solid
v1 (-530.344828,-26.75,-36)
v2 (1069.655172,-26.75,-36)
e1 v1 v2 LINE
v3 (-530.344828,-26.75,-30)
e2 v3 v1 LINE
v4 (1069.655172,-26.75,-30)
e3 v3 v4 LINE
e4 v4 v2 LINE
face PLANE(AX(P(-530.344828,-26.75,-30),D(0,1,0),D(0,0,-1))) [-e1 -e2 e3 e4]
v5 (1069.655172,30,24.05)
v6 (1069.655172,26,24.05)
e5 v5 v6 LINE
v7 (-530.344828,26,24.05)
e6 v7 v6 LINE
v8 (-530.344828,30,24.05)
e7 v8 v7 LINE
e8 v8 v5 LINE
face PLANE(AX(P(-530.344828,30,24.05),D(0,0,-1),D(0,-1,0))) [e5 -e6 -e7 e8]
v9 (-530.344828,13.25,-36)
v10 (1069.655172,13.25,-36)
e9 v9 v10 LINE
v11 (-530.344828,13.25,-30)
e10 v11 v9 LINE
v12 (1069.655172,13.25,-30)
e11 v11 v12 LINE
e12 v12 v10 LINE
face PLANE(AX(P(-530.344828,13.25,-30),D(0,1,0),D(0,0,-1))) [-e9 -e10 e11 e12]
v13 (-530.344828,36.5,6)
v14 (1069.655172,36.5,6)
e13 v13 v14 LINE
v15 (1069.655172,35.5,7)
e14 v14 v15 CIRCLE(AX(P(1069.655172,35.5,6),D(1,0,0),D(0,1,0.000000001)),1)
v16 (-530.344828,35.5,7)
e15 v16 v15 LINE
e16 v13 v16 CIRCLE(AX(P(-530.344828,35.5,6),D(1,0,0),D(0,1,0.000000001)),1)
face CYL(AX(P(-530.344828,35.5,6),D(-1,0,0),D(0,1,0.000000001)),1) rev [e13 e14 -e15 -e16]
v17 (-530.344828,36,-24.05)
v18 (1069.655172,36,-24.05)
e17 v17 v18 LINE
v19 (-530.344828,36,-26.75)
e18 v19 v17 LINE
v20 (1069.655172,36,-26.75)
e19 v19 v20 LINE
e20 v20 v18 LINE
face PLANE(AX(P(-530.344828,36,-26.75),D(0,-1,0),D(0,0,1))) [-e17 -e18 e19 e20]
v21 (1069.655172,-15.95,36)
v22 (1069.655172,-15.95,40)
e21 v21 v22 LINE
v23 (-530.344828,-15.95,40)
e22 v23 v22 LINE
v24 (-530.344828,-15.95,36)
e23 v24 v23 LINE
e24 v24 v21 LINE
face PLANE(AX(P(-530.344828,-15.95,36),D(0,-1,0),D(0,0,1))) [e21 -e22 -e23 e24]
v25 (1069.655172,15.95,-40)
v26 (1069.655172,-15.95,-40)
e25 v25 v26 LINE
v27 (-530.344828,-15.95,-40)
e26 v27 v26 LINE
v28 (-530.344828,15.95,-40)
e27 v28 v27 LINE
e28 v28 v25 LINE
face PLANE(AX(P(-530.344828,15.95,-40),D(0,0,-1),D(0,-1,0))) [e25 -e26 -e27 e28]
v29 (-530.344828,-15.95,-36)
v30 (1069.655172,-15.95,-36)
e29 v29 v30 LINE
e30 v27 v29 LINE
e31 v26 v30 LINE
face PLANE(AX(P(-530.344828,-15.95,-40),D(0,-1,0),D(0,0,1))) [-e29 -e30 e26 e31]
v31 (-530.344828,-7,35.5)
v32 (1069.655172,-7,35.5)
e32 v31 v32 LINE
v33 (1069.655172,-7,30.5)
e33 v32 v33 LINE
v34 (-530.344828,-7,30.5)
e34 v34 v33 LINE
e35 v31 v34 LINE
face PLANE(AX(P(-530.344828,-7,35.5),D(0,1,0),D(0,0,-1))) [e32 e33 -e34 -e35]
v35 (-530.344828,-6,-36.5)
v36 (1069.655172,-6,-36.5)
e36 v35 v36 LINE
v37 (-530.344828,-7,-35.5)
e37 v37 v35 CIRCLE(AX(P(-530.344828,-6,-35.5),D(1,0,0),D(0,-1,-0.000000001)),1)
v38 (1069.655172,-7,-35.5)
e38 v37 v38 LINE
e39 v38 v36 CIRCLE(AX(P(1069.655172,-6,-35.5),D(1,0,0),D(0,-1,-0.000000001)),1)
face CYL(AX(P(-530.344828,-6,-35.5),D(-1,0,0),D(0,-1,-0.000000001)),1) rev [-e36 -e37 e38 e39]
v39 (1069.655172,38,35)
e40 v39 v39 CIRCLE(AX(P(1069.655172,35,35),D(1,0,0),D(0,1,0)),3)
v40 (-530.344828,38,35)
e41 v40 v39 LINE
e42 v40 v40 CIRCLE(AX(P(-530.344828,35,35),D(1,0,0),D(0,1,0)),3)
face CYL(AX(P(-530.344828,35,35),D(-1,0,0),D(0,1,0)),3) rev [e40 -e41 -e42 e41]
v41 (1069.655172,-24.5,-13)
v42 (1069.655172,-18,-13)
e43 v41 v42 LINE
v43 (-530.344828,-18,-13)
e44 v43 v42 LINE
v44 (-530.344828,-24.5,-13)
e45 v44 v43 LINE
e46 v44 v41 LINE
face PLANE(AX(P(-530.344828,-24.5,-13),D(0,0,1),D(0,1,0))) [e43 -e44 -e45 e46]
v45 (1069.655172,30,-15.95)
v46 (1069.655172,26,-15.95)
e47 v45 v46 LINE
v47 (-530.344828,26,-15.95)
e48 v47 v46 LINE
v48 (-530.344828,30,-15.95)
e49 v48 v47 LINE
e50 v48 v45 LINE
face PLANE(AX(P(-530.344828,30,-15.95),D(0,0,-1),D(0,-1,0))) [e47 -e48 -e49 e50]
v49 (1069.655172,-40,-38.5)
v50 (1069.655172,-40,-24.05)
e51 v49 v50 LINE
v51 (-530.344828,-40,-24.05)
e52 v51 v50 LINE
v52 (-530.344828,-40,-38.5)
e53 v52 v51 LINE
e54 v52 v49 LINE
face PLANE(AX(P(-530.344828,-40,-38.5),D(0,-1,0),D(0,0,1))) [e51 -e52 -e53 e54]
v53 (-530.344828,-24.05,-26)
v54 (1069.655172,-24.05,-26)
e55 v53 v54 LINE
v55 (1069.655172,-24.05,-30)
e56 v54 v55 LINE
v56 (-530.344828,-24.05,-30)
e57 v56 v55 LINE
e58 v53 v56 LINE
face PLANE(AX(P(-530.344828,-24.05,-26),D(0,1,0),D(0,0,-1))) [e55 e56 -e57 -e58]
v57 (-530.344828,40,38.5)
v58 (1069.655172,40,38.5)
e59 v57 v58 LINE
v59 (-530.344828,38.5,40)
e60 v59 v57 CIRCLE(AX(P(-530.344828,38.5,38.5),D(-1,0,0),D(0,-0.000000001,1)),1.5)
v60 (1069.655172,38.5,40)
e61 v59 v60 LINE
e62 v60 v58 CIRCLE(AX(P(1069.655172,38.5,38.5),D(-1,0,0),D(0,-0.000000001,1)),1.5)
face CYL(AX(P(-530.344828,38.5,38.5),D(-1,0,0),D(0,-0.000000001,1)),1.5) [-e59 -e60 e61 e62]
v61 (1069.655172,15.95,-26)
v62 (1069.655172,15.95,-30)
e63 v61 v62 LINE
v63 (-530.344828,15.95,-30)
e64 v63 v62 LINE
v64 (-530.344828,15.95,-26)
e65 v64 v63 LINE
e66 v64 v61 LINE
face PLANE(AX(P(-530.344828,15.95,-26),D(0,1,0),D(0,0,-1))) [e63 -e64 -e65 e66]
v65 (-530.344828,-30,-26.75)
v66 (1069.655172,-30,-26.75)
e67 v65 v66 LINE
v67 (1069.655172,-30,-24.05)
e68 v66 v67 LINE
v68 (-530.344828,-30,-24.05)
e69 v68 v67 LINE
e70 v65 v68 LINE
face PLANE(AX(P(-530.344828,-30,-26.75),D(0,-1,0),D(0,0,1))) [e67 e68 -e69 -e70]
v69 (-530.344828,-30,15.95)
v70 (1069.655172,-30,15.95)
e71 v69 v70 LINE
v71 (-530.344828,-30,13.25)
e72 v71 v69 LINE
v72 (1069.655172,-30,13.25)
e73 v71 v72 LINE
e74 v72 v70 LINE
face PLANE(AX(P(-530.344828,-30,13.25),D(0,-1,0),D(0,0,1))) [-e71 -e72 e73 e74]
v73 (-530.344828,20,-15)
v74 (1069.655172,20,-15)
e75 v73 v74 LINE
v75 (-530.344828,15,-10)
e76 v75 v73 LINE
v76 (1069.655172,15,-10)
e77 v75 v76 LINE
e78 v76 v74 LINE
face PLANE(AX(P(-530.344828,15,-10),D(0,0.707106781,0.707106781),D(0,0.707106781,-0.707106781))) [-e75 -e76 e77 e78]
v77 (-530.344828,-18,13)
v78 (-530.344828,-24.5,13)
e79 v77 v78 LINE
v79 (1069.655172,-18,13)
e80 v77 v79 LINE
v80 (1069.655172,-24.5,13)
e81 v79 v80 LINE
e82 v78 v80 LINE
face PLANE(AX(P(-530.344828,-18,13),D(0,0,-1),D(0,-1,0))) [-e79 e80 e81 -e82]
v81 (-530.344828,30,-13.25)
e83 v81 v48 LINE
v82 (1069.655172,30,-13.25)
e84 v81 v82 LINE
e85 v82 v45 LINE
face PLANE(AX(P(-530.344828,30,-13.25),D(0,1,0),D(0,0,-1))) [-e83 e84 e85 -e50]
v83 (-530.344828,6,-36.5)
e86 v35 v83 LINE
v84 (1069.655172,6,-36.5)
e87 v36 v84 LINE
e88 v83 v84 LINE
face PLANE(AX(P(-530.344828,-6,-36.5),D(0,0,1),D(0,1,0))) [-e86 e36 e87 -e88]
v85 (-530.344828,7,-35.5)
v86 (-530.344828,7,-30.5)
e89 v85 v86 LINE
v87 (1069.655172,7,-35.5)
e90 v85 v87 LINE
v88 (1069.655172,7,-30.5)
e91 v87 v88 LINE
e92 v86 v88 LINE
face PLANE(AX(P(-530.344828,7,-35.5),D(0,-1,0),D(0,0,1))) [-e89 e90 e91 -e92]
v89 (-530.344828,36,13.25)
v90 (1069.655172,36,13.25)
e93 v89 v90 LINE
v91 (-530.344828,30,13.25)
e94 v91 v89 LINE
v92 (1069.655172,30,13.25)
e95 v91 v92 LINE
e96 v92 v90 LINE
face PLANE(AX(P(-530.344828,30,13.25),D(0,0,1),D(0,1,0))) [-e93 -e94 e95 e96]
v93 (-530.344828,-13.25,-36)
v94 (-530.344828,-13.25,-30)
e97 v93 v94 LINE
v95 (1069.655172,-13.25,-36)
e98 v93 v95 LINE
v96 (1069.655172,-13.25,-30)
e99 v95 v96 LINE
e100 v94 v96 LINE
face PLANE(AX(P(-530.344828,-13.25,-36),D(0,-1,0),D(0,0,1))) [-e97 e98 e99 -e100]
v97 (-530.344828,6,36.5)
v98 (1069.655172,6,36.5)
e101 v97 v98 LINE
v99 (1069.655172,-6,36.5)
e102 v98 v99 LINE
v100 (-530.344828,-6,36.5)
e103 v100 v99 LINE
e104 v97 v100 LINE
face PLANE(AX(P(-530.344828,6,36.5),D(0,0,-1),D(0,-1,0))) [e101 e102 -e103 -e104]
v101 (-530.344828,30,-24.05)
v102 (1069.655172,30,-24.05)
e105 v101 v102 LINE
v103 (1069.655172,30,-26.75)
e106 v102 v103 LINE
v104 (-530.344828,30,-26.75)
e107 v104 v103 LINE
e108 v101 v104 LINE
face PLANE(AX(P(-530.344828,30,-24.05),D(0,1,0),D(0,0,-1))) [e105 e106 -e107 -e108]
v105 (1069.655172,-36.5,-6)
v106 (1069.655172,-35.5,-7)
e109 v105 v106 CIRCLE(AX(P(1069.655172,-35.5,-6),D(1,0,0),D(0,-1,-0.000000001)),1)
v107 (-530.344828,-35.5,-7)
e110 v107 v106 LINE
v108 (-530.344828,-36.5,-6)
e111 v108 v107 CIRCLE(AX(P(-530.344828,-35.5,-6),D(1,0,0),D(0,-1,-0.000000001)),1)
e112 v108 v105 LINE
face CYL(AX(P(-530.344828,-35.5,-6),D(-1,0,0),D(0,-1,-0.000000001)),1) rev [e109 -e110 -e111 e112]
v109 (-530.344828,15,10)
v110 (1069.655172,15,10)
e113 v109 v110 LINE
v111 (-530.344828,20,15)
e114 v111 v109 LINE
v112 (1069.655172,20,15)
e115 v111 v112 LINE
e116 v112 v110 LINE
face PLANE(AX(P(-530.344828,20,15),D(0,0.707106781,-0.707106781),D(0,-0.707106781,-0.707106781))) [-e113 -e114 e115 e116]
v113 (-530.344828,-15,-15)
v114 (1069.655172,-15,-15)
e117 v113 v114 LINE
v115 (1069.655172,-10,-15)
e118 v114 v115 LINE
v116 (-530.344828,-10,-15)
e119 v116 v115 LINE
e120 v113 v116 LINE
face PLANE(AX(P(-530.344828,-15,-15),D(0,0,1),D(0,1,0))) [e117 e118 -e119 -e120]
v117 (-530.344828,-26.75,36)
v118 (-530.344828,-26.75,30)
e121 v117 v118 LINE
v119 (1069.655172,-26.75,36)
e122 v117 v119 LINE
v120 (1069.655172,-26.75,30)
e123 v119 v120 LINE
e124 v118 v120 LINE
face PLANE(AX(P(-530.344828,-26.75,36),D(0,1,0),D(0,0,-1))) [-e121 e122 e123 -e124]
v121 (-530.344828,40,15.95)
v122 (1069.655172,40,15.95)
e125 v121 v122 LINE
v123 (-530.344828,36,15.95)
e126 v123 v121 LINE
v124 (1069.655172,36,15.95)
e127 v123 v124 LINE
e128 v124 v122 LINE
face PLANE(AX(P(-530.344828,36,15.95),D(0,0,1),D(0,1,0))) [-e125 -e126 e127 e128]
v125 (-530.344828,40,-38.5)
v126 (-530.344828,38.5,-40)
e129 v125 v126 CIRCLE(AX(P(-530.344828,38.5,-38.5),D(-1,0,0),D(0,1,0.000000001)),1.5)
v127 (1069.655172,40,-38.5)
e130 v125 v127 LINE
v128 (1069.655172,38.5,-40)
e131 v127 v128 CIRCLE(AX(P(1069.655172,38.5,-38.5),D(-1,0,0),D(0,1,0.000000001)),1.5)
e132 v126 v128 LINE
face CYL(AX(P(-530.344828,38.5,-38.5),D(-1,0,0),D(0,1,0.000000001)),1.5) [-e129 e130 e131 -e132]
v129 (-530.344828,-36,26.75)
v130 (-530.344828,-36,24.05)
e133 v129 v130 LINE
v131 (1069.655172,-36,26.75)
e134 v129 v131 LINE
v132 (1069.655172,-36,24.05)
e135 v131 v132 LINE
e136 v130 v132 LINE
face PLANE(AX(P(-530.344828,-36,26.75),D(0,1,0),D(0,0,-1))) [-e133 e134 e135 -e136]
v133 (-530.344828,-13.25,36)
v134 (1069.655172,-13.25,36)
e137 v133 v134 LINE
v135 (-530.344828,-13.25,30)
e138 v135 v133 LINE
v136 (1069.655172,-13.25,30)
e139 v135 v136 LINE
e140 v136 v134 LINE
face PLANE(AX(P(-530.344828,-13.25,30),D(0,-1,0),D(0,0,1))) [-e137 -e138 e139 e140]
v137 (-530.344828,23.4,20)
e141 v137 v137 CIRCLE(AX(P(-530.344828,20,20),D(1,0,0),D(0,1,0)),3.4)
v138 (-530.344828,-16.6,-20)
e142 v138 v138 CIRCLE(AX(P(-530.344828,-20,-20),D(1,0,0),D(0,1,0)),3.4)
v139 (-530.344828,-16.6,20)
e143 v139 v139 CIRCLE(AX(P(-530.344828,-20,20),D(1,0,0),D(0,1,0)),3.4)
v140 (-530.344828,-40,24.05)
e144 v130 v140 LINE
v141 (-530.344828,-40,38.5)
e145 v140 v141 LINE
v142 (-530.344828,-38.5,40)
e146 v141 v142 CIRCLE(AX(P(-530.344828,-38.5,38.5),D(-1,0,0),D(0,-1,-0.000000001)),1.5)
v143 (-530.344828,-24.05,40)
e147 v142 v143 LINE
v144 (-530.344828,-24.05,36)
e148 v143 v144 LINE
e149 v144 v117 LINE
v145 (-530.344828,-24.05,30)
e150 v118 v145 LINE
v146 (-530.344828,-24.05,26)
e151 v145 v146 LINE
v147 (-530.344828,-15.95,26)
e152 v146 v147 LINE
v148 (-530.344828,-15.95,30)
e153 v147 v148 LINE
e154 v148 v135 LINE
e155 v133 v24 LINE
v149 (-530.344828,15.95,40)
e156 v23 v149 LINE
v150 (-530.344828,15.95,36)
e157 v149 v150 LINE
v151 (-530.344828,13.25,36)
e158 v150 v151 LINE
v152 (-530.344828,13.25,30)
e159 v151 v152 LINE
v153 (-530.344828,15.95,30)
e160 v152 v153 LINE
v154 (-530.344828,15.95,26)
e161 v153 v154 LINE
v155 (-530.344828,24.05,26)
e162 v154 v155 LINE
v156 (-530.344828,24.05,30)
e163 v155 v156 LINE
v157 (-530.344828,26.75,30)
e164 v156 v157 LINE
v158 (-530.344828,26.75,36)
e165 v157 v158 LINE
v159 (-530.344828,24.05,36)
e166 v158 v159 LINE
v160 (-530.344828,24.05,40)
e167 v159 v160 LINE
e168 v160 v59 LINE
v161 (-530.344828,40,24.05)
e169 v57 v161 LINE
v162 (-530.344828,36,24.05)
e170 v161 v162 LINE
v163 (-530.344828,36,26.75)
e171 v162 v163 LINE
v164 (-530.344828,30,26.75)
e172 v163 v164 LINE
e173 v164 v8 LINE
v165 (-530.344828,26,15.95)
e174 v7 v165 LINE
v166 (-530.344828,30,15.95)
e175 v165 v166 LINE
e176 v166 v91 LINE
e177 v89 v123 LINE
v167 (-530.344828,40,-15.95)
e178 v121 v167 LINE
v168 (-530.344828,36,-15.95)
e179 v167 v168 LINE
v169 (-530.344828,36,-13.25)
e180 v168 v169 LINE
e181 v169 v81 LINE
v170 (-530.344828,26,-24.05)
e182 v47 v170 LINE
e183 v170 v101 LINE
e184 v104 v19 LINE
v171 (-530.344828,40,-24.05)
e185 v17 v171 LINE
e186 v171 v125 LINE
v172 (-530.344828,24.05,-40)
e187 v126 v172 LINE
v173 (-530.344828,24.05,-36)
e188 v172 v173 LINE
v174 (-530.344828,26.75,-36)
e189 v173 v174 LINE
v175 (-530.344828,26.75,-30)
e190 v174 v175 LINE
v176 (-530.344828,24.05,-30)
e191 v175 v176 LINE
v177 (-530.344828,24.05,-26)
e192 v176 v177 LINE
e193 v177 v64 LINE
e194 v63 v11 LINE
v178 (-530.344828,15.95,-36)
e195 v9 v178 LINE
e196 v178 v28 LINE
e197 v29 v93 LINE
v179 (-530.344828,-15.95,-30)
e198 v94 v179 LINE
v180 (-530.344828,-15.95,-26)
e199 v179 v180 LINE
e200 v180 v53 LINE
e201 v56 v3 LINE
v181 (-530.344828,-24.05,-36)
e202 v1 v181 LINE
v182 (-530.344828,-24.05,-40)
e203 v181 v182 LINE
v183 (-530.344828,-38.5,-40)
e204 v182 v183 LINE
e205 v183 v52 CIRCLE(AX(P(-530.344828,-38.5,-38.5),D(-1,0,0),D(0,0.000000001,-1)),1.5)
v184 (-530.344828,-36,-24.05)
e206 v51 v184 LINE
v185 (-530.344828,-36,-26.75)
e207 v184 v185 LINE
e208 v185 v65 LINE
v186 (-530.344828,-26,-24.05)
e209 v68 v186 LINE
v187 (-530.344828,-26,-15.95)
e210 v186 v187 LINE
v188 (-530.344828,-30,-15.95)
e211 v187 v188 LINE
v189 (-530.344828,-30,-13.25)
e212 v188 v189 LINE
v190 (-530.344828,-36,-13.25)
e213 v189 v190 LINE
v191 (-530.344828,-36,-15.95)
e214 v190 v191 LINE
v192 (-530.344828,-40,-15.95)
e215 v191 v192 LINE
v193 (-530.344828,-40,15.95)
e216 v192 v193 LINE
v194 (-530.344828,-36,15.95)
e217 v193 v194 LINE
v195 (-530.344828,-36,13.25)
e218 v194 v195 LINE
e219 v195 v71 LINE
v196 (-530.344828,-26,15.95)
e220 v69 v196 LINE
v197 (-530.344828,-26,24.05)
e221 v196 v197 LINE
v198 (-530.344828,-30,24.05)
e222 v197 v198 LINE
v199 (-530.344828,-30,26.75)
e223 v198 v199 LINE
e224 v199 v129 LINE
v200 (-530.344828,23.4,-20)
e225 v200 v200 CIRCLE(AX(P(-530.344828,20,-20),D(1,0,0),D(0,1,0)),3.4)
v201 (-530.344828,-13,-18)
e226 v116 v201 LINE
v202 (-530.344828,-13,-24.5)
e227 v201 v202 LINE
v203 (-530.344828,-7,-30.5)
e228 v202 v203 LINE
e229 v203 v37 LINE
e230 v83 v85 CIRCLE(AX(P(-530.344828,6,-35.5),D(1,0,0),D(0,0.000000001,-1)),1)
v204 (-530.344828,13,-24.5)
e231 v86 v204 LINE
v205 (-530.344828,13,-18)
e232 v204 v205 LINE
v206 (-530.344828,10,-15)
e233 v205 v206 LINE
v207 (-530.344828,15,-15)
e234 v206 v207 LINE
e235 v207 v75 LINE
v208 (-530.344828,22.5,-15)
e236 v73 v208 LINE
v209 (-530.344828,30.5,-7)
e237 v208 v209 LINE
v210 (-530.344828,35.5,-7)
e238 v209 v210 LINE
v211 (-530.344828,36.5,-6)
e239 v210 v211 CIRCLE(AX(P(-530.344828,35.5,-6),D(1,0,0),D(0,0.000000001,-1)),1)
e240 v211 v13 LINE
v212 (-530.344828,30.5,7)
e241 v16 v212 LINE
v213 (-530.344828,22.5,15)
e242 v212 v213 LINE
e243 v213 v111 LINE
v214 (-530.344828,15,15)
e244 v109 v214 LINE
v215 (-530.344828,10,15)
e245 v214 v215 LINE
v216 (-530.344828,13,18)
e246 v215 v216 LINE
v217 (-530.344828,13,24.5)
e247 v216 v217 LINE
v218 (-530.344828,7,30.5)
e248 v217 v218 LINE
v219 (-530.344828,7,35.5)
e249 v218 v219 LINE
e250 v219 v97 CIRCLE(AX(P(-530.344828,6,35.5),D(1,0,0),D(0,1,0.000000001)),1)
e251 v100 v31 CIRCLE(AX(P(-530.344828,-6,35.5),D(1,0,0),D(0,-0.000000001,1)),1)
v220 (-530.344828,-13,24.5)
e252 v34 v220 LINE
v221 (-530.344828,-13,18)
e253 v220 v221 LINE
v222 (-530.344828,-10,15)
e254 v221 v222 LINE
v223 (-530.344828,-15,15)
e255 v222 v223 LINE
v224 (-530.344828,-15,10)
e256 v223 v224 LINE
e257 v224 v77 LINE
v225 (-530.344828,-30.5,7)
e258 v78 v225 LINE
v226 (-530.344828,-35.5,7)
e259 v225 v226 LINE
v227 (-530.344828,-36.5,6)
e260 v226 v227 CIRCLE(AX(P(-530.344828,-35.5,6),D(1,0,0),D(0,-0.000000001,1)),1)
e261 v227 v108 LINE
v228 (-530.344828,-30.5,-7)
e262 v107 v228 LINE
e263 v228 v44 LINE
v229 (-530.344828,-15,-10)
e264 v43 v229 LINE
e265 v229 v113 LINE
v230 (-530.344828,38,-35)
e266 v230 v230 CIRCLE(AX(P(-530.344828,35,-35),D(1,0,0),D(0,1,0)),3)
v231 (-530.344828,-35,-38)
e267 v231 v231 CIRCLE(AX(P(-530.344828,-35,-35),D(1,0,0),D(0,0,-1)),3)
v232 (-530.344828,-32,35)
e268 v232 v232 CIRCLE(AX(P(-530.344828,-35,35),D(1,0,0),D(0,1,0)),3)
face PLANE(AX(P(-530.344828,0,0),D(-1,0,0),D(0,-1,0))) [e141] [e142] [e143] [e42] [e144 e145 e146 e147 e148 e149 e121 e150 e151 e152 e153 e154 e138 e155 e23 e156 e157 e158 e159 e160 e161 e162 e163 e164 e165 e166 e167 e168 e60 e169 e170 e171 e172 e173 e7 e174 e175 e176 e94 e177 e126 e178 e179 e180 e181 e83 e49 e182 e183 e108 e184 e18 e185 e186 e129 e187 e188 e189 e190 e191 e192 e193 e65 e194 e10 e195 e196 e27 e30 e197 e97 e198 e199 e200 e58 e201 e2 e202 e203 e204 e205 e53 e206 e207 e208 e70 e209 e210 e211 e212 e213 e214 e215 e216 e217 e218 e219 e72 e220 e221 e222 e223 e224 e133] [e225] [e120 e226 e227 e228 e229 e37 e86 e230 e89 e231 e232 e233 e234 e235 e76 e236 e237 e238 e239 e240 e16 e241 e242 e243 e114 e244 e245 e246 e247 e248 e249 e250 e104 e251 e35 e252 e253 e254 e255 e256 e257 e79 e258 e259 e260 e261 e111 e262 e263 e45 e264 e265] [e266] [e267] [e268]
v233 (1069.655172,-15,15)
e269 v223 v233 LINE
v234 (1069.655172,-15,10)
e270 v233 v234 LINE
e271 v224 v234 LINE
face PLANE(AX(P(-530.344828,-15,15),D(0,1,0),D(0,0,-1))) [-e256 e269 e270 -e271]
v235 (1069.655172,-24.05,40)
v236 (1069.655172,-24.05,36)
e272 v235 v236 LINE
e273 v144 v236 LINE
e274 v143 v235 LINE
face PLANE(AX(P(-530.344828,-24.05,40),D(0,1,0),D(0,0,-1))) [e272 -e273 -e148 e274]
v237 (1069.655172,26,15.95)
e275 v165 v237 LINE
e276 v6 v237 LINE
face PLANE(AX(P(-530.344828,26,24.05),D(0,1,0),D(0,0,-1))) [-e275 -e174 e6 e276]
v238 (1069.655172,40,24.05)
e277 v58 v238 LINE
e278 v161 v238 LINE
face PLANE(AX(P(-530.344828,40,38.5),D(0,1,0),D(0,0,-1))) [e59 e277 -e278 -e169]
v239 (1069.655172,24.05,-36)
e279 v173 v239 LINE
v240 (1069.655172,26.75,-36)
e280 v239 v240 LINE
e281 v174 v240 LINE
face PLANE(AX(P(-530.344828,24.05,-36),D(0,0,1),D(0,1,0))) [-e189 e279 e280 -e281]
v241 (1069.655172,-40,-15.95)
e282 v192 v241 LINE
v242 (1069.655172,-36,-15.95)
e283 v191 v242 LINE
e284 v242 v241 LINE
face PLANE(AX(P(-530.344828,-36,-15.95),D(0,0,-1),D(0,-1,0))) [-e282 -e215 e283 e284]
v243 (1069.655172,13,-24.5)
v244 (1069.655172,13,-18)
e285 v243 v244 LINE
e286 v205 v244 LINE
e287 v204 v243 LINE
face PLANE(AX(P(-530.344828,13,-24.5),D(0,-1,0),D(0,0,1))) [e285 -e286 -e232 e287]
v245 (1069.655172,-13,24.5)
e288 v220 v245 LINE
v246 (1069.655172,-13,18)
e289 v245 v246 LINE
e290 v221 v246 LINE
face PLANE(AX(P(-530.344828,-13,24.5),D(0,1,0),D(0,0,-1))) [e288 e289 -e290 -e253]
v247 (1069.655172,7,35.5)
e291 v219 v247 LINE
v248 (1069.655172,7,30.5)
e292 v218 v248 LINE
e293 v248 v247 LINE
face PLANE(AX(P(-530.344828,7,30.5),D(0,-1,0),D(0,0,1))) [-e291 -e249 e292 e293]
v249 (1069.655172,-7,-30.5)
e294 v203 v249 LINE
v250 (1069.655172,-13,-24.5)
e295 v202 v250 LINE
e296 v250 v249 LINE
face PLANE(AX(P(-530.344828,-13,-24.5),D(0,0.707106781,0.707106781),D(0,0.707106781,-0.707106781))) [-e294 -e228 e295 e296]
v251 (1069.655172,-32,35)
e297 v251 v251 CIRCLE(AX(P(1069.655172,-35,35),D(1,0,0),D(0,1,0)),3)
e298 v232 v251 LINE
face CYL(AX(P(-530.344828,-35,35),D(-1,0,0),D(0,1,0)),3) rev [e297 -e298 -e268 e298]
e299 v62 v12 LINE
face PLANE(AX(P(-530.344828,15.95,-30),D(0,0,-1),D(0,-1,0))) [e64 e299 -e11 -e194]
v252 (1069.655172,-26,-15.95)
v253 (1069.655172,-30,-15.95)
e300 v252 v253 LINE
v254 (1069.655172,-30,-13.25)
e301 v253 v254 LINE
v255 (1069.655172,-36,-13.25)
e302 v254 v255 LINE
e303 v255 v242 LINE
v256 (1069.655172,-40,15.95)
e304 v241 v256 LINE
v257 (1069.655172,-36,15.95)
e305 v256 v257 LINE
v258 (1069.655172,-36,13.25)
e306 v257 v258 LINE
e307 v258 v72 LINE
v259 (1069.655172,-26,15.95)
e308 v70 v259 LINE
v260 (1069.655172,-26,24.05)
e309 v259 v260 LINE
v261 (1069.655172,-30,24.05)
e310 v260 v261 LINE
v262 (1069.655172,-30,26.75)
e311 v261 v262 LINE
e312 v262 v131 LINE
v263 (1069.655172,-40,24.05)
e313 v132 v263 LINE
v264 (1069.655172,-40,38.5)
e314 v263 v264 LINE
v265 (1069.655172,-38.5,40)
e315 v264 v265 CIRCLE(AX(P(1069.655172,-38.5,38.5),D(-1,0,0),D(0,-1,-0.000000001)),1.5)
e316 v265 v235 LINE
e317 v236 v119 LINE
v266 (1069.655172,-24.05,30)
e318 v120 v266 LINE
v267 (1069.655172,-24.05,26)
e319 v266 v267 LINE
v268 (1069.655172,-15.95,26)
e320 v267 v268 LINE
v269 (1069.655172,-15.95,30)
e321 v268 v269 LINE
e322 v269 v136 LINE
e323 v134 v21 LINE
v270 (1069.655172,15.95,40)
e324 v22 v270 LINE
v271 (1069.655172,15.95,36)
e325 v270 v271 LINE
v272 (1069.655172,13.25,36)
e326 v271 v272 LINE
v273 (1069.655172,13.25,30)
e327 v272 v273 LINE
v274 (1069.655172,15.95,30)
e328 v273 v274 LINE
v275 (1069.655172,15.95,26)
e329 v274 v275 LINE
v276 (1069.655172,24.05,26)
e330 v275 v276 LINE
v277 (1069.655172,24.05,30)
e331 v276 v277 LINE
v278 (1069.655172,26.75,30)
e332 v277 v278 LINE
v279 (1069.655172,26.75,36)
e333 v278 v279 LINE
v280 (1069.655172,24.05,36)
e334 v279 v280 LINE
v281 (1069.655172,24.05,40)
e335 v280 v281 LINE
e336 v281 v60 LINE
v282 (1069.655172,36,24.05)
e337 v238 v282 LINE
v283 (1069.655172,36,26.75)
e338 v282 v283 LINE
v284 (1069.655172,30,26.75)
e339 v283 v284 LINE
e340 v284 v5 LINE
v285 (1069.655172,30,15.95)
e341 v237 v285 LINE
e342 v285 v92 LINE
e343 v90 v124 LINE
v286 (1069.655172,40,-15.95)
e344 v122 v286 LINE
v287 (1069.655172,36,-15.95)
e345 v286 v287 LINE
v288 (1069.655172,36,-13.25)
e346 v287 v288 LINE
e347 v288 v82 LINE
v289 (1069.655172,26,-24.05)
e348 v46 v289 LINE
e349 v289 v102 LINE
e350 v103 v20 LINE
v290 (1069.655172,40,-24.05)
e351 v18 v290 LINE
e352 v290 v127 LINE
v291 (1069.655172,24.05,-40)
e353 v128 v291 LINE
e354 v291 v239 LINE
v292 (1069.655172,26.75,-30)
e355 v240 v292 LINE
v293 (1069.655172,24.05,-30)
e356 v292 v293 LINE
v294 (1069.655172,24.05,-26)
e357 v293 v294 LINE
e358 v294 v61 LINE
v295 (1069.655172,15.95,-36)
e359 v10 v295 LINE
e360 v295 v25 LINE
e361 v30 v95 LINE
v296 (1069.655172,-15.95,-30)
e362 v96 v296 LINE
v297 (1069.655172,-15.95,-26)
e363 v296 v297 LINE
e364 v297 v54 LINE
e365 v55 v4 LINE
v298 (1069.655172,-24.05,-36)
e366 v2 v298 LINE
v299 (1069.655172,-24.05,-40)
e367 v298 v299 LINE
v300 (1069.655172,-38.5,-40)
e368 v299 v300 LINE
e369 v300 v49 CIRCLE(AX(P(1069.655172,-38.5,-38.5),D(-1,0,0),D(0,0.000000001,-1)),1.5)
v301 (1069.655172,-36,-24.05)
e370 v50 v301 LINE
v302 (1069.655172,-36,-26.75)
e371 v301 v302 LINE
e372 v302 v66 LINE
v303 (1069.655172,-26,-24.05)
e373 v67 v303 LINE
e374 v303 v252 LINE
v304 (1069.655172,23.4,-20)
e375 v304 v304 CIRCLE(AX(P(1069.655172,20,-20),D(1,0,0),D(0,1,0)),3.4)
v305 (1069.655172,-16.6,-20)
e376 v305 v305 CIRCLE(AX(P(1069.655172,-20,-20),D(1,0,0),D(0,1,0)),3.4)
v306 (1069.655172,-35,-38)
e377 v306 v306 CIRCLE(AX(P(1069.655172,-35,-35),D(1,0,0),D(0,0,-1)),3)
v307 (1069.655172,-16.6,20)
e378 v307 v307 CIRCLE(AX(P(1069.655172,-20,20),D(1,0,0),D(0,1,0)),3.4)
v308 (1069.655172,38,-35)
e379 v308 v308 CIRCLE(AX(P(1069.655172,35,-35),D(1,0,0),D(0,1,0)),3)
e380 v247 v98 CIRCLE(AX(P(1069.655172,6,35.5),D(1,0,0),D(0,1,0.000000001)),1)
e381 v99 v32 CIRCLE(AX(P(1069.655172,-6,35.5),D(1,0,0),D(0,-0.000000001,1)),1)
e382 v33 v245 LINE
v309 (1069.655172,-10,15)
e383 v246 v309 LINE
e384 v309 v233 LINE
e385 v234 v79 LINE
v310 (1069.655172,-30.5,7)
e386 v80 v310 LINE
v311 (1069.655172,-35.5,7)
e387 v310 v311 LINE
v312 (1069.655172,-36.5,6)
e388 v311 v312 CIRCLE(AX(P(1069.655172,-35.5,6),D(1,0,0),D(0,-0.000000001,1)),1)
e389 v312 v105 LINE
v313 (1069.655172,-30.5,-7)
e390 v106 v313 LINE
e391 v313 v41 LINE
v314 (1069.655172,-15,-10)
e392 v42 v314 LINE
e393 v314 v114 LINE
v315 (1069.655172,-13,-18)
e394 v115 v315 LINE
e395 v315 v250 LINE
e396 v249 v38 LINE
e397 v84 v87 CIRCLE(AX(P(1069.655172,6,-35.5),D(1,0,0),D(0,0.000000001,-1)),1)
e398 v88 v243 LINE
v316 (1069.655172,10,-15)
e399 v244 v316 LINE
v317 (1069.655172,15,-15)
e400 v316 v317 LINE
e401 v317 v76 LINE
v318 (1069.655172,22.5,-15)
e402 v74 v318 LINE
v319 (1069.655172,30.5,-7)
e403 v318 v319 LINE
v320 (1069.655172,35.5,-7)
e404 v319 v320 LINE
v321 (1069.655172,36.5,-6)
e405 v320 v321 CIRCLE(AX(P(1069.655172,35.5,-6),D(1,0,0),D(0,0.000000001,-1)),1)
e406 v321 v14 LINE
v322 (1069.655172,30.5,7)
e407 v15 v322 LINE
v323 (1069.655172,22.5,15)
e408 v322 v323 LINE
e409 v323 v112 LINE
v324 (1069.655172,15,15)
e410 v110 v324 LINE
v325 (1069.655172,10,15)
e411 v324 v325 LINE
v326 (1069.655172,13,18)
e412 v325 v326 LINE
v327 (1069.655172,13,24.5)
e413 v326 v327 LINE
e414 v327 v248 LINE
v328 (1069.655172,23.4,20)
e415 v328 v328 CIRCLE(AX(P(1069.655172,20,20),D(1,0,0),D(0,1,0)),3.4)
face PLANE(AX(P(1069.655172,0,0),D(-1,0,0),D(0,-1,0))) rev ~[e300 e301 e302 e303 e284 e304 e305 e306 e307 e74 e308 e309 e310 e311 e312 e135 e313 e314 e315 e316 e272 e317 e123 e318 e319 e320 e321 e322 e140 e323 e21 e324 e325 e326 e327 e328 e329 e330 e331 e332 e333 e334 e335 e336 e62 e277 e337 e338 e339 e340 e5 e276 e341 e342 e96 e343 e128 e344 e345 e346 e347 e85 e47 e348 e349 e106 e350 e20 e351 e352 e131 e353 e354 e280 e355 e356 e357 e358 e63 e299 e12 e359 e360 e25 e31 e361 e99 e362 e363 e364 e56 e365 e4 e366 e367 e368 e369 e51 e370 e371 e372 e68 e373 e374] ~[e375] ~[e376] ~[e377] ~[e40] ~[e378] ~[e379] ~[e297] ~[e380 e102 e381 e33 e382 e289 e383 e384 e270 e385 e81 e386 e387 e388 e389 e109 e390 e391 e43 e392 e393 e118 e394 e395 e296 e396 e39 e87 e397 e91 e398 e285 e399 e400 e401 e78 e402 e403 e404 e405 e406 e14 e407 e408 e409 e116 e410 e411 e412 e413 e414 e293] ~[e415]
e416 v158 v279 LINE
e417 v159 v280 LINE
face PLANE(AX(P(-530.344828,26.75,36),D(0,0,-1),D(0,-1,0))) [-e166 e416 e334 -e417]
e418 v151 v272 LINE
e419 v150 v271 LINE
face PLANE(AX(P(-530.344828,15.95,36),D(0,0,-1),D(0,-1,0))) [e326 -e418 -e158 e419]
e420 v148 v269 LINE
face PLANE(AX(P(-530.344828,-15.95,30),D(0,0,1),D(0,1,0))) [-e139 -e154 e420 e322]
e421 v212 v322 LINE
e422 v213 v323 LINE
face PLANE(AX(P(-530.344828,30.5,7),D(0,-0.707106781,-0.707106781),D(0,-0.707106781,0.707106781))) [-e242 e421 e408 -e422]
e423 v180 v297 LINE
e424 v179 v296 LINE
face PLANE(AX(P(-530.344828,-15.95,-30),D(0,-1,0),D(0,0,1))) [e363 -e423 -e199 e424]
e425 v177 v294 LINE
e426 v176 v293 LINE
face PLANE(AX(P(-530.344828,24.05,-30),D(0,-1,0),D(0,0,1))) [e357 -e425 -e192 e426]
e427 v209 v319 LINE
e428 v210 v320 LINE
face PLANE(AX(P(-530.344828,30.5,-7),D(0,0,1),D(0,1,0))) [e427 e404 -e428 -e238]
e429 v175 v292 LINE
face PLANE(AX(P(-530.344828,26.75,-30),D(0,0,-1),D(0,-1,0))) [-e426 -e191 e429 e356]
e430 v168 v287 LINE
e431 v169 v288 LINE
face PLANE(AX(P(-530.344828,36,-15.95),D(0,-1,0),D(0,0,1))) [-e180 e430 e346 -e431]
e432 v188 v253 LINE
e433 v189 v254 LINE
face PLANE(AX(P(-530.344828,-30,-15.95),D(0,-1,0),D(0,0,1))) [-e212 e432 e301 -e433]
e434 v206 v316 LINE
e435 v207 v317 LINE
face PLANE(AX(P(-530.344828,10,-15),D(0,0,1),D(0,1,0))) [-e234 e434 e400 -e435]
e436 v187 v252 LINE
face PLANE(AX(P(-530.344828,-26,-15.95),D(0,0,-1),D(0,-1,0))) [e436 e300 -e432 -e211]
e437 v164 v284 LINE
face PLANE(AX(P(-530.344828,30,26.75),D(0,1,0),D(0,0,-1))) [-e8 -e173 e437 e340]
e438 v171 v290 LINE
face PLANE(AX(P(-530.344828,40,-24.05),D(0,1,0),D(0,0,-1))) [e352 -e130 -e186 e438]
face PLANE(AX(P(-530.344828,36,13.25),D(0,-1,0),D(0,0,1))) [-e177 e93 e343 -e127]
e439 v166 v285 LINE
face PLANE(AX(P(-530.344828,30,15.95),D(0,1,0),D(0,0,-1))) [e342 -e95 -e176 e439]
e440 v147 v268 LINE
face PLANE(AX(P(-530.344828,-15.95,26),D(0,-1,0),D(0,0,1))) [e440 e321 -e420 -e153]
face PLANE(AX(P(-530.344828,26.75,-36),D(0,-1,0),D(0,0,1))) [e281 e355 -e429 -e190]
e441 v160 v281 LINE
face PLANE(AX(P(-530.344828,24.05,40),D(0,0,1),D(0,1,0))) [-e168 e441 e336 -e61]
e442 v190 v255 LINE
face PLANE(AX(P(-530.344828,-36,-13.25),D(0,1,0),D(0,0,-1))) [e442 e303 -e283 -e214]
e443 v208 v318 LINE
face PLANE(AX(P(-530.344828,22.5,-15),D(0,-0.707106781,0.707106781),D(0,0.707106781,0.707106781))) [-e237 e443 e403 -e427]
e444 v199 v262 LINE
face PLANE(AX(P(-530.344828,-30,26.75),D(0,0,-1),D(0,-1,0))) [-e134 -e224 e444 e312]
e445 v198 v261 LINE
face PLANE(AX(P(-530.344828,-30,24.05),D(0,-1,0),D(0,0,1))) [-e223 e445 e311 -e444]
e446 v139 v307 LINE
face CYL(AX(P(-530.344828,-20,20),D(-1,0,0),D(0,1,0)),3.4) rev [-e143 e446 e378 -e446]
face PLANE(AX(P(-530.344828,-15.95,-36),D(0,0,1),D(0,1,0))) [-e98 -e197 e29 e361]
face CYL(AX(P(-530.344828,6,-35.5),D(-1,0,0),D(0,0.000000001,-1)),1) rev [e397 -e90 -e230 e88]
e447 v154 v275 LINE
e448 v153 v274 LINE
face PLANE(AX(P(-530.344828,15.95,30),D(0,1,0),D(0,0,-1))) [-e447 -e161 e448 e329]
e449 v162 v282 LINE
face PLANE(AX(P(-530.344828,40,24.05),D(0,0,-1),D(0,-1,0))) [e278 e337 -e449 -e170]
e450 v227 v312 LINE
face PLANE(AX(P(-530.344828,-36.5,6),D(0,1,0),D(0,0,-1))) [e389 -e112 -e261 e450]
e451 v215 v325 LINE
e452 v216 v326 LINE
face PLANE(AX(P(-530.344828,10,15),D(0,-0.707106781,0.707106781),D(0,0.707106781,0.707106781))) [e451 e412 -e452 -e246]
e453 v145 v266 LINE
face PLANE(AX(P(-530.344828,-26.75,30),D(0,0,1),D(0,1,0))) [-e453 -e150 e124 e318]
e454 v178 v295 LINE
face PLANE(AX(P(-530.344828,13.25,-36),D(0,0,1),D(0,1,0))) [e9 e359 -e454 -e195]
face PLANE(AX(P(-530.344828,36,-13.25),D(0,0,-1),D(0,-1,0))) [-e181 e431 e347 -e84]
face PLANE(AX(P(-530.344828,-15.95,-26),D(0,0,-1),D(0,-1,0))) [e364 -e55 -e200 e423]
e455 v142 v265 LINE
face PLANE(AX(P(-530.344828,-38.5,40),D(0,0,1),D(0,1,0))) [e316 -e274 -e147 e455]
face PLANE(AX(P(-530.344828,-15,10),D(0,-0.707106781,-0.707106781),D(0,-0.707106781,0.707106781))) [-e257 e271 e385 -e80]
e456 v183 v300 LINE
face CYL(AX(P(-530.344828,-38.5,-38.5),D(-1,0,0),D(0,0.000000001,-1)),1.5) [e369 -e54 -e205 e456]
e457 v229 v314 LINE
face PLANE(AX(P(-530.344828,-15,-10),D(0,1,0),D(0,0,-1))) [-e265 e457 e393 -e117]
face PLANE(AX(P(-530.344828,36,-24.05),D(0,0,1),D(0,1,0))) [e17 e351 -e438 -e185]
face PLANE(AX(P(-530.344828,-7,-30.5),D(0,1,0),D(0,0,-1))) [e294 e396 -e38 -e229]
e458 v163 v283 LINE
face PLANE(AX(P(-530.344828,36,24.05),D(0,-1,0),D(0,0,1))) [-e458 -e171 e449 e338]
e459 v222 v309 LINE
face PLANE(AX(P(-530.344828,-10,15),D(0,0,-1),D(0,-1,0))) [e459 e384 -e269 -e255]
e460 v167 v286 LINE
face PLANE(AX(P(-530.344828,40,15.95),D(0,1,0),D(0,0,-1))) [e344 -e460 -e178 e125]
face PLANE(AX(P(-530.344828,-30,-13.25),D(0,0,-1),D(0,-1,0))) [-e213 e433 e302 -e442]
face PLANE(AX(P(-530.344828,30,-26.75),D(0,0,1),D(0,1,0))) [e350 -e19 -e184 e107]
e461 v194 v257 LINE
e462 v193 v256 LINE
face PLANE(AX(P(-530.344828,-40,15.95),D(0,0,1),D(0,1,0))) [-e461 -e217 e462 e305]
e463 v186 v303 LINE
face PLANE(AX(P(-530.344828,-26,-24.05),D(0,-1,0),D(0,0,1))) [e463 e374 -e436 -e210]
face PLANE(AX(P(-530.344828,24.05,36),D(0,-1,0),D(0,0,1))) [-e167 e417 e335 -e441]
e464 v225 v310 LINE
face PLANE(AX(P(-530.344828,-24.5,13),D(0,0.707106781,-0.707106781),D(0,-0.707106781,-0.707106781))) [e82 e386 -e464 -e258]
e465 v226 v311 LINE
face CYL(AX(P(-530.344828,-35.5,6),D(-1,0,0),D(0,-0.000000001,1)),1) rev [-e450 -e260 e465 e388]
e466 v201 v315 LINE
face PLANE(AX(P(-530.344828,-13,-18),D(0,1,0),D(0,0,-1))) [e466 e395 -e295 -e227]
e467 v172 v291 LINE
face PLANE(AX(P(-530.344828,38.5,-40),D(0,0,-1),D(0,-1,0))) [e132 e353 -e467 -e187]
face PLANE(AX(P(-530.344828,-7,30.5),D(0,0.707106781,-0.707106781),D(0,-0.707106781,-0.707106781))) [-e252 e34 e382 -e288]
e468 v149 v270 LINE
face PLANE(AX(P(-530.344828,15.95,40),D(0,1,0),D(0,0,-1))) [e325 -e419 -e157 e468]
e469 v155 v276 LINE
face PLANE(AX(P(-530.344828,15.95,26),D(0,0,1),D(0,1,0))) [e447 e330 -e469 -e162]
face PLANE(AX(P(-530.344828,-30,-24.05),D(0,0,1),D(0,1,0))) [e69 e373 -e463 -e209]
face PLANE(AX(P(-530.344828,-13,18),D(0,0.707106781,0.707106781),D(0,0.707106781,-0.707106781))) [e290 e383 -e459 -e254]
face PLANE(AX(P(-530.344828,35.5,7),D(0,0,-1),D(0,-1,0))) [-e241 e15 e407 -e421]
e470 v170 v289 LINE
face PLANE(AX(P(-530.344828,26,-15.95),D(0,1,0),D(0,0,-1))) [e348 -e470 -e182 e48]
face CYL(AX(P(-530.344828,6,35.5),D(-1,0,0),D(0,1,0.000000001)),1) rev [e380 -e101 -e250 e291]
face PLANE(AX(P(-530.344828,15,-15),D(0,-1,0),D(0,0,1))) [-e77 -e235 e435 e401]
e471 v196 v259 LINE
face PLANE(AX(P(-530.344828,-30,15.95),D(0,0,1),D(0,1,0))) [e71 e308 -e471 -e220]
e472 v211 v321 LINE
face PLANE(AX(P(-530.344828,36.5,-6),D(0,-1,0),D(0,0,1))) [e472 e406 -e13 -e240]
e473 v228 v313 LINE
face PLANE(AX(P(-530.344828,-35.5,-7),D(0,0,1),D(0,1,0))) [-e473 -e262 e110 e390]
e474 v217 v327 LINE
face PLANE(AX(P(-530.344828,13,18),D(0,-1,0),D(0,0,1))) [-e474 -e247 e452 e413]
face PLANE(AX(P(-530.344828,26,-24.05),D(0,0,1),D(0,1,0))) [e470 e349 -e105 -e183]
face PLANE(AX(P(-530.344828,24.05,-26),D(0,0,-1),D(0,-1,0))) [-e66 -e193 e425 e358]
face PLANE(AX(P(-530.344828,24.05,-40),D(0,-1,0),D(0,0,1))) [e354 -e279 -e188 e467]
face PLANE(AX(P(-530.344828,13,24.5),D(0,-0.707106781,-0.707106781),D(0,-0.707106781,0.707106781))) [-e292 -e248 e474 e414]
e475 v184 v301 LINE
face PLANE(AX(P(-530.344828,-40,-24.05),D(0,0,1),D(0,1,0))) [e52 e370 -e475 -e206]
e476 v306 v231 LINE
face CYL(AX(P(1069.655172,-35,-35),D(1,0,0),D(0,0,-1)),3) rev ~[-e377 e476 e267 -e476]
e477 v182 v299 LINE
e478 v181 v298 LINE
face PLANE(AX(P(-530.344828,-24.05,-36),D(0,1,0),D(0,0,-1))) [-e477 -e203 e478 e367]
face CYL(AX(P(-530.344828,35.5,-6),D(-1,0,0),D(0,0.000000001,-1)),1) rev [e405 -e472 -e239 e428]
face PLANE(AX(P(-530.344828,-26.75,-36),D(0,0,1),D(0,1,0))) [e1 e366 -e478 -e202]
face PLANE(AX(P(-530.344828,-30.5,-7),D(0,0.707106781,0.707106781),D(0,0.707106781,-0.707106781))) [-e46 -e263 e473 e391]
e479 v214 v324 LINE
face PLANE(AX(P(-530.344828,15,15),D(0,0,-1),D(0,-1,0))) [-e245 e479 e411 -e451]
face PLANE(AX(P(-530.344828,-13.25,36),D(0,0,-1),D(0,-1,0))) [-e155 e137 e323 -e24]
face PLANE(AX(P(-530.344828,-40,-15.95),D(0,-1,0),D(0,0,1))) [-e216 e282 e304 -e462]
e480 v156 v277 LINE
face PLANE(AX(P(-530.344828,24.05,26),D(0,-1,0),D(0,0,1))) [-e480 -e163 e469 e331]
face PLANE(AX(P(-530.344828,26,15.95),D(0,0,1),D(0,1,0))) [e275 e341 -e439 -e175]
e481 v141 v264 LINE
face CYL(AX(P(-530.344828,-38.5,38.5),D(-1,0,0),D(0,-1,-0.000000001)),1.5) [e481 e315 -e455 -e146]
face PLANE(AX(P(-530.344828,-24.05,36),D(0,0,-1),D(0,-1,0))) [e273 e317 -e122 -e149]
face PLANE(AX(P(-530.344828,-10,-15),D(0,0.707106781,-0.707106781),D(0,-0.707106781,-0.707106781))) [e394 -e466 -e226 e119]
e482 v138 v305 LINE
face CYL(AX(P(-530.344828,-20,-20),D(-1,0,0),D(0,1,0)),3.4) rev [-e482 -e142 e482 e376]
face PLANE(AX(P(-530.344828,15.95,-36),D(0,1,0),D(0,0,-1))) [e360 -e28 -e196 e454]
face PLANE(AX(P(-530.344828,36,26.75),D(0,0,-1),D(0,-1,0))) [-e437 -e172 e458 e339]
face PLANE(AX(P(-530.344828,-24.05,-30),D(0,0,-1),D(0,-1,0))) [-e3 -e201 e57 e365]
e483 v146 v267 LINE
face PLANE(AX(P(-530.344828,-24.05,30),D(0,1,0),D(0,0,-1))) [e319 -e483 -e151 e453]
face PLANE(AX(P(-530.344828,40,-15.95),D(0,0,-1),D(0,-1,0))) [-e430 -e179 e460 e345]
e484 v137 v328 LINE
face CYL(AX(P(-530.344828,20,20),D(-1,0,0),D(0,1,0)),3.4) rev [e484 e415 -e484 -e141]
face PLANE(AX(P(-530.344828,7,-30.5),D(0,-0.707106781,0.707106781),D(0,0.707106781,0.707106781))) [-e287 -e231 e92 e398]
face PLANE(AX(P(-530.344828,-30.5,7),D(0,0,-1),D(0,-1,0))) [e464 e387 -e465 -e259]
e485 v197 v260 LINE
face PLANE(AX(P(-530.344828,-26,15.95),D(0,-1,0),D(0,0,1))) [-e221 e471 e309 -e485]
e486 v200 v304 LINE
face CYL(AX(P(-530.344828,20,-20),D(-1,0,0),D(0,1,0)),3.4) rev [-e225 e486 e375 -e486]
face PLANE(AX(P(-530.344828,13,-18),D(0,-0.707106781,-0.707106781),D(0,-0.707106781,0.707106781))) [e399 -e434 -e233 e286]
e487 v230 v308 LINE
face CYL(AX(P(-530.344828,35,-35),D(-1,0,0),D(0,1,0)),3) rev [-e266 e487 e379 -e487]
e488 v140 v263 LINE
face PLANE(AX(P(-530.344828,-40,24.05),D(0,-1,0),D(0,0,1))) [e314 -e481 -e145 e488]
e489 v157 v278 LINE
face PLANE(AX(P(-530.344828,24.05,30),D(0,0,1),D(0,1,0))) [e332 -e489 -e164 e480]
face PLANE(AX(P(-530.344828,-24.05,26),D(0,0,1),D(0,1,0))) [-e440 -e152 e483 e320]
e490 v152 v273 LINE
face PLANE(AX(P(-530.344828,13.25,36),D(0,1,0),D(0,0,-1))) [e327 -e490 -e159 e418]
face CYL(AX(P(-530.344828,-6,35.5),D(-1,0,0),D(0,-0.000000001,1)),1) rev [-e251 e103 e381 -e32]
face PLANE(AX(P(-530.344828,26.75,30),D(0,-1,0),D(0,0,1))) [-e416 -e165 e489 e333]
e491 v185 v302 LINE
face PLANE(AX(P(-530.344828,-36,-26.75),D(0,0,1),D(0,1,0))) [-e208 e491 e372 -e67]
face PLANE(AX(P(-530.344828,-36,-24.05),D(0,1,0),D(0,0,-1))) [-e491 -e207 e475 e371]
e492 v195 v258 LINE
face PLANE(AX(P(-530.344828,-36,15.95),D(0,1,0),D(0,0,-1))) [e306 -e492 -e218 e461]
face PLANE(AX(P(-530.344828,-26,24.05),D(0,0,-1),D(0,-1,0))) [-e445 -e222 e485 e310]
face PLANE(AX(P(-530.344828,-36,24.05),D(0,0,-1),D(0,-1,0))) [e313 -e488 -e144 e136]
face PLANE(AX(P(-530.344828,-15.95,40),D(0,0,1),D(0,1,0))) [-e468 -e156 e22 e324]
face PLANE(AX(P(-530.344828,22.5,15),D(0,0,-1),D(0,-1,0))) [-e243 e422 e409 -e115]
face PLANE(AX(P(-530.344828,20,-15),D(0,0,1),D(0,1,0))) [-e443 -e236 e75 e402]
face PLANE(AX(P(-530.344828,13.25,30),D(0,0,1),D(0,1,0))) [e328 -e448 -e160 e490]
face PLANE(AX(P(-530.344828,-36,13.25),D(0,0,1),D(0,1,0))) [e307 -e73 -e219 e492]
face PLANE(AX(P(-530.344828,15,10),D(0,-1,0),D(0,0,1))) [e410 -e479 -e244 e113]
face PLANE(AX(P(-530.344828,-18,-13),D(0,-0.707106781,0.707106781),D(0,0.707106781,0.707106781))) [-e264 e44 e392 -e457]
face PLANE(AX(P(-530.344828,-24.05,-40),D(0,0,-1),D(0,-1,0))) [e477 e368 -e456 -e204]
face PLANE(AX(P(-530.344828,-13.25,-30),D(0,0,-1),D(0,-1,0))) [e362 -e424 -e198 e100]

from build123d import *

# Parameters (mm, degrees)
SKETCH1_R                                = 3.4
SKETCH1_R_2                              = 3
ALUMINUM_PROFILE_80_X_80G_X_R1_5_1_DEPTH = 1600
SKETCH10_R                               = 3
CUT_EXTRUDE1_DEPTH                       = 1601.999687695


with BuildPart() as part:
    # Sketch1 → Aluminum profile 80 X 80G X R1.5(1) (new body)
    with BuildSketch(Plane.YZ.offset(-530.344827586)):
        with BuildLine():
            Line((-24.05, 40), (-24.05, 36))
            Line((-24.05, 36), (-26.75, 36))
            Line((-26.75, 36), (-26.75, 30))
            Line((-26.75, 30), (-24.05, 30))
            Line((-24.05, 30), (-24.05, 26))
            Line((-24.05, 26), (-15.95, 26))
            Line((-15.95, 26), (-15.95, 30))
            Line((-15.95, 30), (-13.25, 30))
            Line((-13.25, 30), (-13.25, 36))
            Line((-13.25, 36), (-15.95, 36))
            Line((-15.95, 36), (-15.95, 40))
            Line((-15.95, 40), (15.95, 40))
            Line((15.95, 40), (15.95, 36))
            Line((15.95, 36), (13.25, 36))
            Line((13.25, 36), (13.25, 30))
            Line((13.25, 30), (15.95, 30))
            Line((15.95, 30), (15.95, 26))
            Line((15.95, 26), (24.05, 26))
            Line((24.05, 26), (24.05, 30))
            Line((24.05, 30), (26.75, 30))
            Line((26.75, 30), (26.75, 36))
            Line((26.75, 36), (24.05, 36))
            Line((24.05, 36), (24.05, 40))
            Line((24.05, 40), (38.5, 40))
            ThreePointArc((38.5, 40), (39.560660172, 39.560660172), (40, 38.5))
            Line((40, 38.5), (40, 24.05))
            Line((40, 24.05), (36, 24.05))
            Line((36, 24.05), (36, 26.75))
            Line((36, 26.75), (30, 26.75))
            Line((30, 26.75), (30, 24.05))
            Line((30, 24.05), (26, 24.05))
            Line((26, 24.05), (26, 15.95))
            Line((26, 15.95), (30, 15.95))
            Line((30, 15.95), (30, 13.25))
            Line((30, 13.25), (36, 13.25))
            Line((36, 13.25), (36, 15.95))
            Line((36, 15.95), (40, 15.95))
            Line((40, 15.95), (40, -15.95))
            Line((40, -15.95), (36, -15.95))
            Line((36, -15.95), (36, -13.25))
            Line((36, -13.25), (30, -13.25))
            Line((30, -13.25), (30, -15.95))
            Line((30, -15.95), (26, -15.95))
            Line((26, -15.95), (26, -24.05))
            Line((26, -24.05), (30, -24.05))
            Line((30, -24.05), (30, -26.75))
            Line((30, -26.75), (36, -26.75))
            Line((36, -26.75), (36, -24.05))
            Line((36, -24.05), (40, -24.05))
            Line((40, -24.05), (40, -38.5))
            ThreePointArc((40, -38.5), (39.560660172, -39.560660172), (38.5, -40))
            Line((38.5, -40), (24.05, -40))
            Line((24.05, -40), (24.05, -36))
            Line((24.05, -36), (26.75, -36))
            Line((26.75, -36), (26.75, -30))
            Line((26.75, -30), (24.05, -30))
            Line((24.05, -30), (24.05, -26))
            Line((24.05, -26), (15.95, -26))
            Line((15.95, -26), (15.95, -30))
            Line((15.95, -30), (13.25, -30))
            Line((13.25, -30), (13.25, -36))
            Line((13.25, -36), (15.95, -36))
            Line((15.95, -36), (15.95, -40))
            Line((15.95, -40), (-15.95, -40))
            Line((-15.95, -40), (-15.95, -36))
            Line((-15.95, -36), (-13.25, -36))
            Line((-13.25, -36), (-13.25, -30))
            Line((-13.25, -30), (-15.95, -30))
            Line((-15.95, -30), (-15.95, -26))
            Line((-15.95, -26), (-24.05, -26))
            Line((-24.05, -26), (-24.05, -30))
            Line((-24.05, -30), (-26.75, -30))
            Line((-26.75, -30), (-26.75, -36))
            Line((-26.75, -36), (-24.05, -36))
            Line((-24.05, -36), (-24.05, -40))
            Line((-24.05, -40), (-38.5, -40))
            ThreePointArc((-38.5, -40), (-39.560660172, -39.560660172), (-40, -38.5))
            Line((-40, -38.5), (-40, -24.05))
            Line((-40, -24.05), (-36, -24.05))
            Line((-36, -24.05), (-36, -26.75))
            Line((-36, -26.75), (-30, -26.75))
            Line((-30, -26.75), (-30, -24.05))
            Line((-30, -24.05), (-26, -24.05))
            Line((-26, -24.05), (-26, -15.95))
            Line((-26, -15.95), (-30, -15.95))
            Line((-30, -15.95), (-30, -13.25))
            Line((-30, -13.25), (-36, -13.25))
            Line((-36, -13.25), (-36, -15.95))
            Line((-36, -15.95), (-40, -15.95))
            Line((-40, -15.95), (-40, 15.95))
            Line((-40, 15.95), (-36, 15.95))
            Line((-36, 15.95), (-36, 13.25))
            Line((-36, 13.25), (-30, 13.25))
            Line((-30, 13.25), (-30, 15.95))
            Line((-30, 15.95), (-26, 15.95))
            Line((-26, 15.95), (-26, 24.05))
            Line((-26, 24.05), (-30, 24.05))
            Line((-30, 24.05), (-30, 26.75))
            Line((-30, 26.75), (-36, 26.75))
            Line((-36, 26.75), (-36, 24.05))
            Line((-36, 24.05), (-40, 24.05))
            Line((-40, 24.05), (-40, 38.5))
            ThreePointArc((-40, 38.5), (-39.560660172, 39.560660172), (-38.5, 40))
            Line((-38.5, 40), (-24.05, 40))
        make_face()
        with Locations((-20, 20)):
            Circle(SKETCH1_R, mode=Mode.SUBTRACT)
        with Locations((20, 20)):
            Circle(SKETCH1_R, mode=Mode.SUBTRACT)
        with Locations((20, -20)):
            Circle(SKETCH1_R, mode=Mode.SUBTRACT)
        with Locations((-20, -20)):
            Circle(SKETCH1_R, mode=Mode.SUBTRACT)
        with Locations((-35, 35)):
            Circle(SKETCH1_R_2, mode=Mode.SUBTRACT)
        with Locations((35, 35)):
            Circle(SKETCH1_R_2, mode=Mode.SUBTRACT)
        with Locations((35, -35)):
            Circle(SKETCH1_R_2, mode=Mode.SUBTRACT)
        with BuildLine():
            Line((-13, 18), (-10, 15))
            Line((-10, 15), (-15, 15))
            Line((-15, 15), (-15, 10))
            Line((-15, 10), (-18, 13))
            Line((-18, 13), (-24.5, 13))
            Line((-24.5, 13), (-30.5, 7))
            Line((-30.5, 7), (-35.5, 7))
            ThreePointArc((-35.5, 7), (-36.207106781, 6.707106781), (-36.5, 6))
            Line((-36.5, 6), (-36.5, -6))
            ThreePointArc((-36.5, -6), (-36.207106781, -6.707106781), (-35.5, -7))
            Line((-35.5, -7), (-30.5, -7))
            Line((-30.5, -7), (-24.5, -13))
            Line((-24.5, -13), (-18, -13))
            Line((-18, -13), (-15, -10))
            Line((-15, -10), (-15, -15))
            Line((-15, -15), (-10, -15))
            Line((-10, -15), (-13, -18))
            Line((-13, -18), (-13, -24.5))
            Line((-13, -24.5), (-7, -30.5))
            Line((-7, -30.5), (-7, -35.5))
            ThreePointArc((-7, -35.5), (-6.707106781, -36.207106781), (-6, -36.5))
            Line((-6, -36.5), (6, -36.5))
            ThreePointArc((6, -36.5), (6.707106781, -36.207106781), (7, -35.5))
            Line((7, -35.5), (7, -30.5))
            Line((7, -30.5), (13, -24.5))
            Line((13, -24.5), (13, -18))
            Line((13, -18), (10, -15))
            Line((10, -15), (15, -15))
            Line((15, -15), (15, -10))
            Line((15, -10), (20, -15))
            Line((20, -15), (22.5, -15))
            Line((22.5, -15), (30.5, -7))
            Line((30.5, -7), (35.5, -7))
            ThreePointArc((35.5, -7), (36.207106781, -6.707106781), (36.5, -6))
            Line((36.5, -6), (36.5, 6))
            ThreePointArc((36.5, 6), (36.207106781, 6.707106781), (35.5, 7))
            Line((35.5, 7), (30.5, 7))
            Line((30.5, 7), (22.5, 15))
            Line((22.5, 15), (20, 15))
            Line((20, 15), (15, 10))
            Line((15, 10), (15, 15))
            Line((15, 15), (10, 15))
            Line((10, 15), (13, 18))
            Line((13, 18), (13, 24.5))
            Line((13, 24.5), (7, 30.5))
            Line((7, 30.5), (7, 35.5))
            ThreePointArc((7, 35.5), (6.707106781, 36.207106781), (6, 36.5))
            Line((6, 36.5), (-6, 36.5))
            ThreePointArc((-6, 36.5), (-6.707106781, 36.207106781), (-7, 35.5))
            Line((-7, 35.5), (-7, 30.5))
            Line((-7, 30.5), (-13, 24.5))
            Line((-13, 24.5), (-13, 18))
        make_face(mode=Mode.SUBTRACT)
    extrude(amount=ALUMINUM_PROFILE_80_X_80G_X_R1_5_1_DEPTH)

    # Sketch10 → Cut-Extrude1 (cut, through all)
    with BuildSketch(Plane(origin=(1069.655172414, 0, 0), x_dir=(0, 0, -1), z_dir=(1, 0, 0))):
        with Locations((35, -35)):
            Circle(SKETCH10_R)
    extrude(amount=-CUT_EXTRUDE1_DEPTH, mode=Mode.SUBTRACT)


solid = part.part
